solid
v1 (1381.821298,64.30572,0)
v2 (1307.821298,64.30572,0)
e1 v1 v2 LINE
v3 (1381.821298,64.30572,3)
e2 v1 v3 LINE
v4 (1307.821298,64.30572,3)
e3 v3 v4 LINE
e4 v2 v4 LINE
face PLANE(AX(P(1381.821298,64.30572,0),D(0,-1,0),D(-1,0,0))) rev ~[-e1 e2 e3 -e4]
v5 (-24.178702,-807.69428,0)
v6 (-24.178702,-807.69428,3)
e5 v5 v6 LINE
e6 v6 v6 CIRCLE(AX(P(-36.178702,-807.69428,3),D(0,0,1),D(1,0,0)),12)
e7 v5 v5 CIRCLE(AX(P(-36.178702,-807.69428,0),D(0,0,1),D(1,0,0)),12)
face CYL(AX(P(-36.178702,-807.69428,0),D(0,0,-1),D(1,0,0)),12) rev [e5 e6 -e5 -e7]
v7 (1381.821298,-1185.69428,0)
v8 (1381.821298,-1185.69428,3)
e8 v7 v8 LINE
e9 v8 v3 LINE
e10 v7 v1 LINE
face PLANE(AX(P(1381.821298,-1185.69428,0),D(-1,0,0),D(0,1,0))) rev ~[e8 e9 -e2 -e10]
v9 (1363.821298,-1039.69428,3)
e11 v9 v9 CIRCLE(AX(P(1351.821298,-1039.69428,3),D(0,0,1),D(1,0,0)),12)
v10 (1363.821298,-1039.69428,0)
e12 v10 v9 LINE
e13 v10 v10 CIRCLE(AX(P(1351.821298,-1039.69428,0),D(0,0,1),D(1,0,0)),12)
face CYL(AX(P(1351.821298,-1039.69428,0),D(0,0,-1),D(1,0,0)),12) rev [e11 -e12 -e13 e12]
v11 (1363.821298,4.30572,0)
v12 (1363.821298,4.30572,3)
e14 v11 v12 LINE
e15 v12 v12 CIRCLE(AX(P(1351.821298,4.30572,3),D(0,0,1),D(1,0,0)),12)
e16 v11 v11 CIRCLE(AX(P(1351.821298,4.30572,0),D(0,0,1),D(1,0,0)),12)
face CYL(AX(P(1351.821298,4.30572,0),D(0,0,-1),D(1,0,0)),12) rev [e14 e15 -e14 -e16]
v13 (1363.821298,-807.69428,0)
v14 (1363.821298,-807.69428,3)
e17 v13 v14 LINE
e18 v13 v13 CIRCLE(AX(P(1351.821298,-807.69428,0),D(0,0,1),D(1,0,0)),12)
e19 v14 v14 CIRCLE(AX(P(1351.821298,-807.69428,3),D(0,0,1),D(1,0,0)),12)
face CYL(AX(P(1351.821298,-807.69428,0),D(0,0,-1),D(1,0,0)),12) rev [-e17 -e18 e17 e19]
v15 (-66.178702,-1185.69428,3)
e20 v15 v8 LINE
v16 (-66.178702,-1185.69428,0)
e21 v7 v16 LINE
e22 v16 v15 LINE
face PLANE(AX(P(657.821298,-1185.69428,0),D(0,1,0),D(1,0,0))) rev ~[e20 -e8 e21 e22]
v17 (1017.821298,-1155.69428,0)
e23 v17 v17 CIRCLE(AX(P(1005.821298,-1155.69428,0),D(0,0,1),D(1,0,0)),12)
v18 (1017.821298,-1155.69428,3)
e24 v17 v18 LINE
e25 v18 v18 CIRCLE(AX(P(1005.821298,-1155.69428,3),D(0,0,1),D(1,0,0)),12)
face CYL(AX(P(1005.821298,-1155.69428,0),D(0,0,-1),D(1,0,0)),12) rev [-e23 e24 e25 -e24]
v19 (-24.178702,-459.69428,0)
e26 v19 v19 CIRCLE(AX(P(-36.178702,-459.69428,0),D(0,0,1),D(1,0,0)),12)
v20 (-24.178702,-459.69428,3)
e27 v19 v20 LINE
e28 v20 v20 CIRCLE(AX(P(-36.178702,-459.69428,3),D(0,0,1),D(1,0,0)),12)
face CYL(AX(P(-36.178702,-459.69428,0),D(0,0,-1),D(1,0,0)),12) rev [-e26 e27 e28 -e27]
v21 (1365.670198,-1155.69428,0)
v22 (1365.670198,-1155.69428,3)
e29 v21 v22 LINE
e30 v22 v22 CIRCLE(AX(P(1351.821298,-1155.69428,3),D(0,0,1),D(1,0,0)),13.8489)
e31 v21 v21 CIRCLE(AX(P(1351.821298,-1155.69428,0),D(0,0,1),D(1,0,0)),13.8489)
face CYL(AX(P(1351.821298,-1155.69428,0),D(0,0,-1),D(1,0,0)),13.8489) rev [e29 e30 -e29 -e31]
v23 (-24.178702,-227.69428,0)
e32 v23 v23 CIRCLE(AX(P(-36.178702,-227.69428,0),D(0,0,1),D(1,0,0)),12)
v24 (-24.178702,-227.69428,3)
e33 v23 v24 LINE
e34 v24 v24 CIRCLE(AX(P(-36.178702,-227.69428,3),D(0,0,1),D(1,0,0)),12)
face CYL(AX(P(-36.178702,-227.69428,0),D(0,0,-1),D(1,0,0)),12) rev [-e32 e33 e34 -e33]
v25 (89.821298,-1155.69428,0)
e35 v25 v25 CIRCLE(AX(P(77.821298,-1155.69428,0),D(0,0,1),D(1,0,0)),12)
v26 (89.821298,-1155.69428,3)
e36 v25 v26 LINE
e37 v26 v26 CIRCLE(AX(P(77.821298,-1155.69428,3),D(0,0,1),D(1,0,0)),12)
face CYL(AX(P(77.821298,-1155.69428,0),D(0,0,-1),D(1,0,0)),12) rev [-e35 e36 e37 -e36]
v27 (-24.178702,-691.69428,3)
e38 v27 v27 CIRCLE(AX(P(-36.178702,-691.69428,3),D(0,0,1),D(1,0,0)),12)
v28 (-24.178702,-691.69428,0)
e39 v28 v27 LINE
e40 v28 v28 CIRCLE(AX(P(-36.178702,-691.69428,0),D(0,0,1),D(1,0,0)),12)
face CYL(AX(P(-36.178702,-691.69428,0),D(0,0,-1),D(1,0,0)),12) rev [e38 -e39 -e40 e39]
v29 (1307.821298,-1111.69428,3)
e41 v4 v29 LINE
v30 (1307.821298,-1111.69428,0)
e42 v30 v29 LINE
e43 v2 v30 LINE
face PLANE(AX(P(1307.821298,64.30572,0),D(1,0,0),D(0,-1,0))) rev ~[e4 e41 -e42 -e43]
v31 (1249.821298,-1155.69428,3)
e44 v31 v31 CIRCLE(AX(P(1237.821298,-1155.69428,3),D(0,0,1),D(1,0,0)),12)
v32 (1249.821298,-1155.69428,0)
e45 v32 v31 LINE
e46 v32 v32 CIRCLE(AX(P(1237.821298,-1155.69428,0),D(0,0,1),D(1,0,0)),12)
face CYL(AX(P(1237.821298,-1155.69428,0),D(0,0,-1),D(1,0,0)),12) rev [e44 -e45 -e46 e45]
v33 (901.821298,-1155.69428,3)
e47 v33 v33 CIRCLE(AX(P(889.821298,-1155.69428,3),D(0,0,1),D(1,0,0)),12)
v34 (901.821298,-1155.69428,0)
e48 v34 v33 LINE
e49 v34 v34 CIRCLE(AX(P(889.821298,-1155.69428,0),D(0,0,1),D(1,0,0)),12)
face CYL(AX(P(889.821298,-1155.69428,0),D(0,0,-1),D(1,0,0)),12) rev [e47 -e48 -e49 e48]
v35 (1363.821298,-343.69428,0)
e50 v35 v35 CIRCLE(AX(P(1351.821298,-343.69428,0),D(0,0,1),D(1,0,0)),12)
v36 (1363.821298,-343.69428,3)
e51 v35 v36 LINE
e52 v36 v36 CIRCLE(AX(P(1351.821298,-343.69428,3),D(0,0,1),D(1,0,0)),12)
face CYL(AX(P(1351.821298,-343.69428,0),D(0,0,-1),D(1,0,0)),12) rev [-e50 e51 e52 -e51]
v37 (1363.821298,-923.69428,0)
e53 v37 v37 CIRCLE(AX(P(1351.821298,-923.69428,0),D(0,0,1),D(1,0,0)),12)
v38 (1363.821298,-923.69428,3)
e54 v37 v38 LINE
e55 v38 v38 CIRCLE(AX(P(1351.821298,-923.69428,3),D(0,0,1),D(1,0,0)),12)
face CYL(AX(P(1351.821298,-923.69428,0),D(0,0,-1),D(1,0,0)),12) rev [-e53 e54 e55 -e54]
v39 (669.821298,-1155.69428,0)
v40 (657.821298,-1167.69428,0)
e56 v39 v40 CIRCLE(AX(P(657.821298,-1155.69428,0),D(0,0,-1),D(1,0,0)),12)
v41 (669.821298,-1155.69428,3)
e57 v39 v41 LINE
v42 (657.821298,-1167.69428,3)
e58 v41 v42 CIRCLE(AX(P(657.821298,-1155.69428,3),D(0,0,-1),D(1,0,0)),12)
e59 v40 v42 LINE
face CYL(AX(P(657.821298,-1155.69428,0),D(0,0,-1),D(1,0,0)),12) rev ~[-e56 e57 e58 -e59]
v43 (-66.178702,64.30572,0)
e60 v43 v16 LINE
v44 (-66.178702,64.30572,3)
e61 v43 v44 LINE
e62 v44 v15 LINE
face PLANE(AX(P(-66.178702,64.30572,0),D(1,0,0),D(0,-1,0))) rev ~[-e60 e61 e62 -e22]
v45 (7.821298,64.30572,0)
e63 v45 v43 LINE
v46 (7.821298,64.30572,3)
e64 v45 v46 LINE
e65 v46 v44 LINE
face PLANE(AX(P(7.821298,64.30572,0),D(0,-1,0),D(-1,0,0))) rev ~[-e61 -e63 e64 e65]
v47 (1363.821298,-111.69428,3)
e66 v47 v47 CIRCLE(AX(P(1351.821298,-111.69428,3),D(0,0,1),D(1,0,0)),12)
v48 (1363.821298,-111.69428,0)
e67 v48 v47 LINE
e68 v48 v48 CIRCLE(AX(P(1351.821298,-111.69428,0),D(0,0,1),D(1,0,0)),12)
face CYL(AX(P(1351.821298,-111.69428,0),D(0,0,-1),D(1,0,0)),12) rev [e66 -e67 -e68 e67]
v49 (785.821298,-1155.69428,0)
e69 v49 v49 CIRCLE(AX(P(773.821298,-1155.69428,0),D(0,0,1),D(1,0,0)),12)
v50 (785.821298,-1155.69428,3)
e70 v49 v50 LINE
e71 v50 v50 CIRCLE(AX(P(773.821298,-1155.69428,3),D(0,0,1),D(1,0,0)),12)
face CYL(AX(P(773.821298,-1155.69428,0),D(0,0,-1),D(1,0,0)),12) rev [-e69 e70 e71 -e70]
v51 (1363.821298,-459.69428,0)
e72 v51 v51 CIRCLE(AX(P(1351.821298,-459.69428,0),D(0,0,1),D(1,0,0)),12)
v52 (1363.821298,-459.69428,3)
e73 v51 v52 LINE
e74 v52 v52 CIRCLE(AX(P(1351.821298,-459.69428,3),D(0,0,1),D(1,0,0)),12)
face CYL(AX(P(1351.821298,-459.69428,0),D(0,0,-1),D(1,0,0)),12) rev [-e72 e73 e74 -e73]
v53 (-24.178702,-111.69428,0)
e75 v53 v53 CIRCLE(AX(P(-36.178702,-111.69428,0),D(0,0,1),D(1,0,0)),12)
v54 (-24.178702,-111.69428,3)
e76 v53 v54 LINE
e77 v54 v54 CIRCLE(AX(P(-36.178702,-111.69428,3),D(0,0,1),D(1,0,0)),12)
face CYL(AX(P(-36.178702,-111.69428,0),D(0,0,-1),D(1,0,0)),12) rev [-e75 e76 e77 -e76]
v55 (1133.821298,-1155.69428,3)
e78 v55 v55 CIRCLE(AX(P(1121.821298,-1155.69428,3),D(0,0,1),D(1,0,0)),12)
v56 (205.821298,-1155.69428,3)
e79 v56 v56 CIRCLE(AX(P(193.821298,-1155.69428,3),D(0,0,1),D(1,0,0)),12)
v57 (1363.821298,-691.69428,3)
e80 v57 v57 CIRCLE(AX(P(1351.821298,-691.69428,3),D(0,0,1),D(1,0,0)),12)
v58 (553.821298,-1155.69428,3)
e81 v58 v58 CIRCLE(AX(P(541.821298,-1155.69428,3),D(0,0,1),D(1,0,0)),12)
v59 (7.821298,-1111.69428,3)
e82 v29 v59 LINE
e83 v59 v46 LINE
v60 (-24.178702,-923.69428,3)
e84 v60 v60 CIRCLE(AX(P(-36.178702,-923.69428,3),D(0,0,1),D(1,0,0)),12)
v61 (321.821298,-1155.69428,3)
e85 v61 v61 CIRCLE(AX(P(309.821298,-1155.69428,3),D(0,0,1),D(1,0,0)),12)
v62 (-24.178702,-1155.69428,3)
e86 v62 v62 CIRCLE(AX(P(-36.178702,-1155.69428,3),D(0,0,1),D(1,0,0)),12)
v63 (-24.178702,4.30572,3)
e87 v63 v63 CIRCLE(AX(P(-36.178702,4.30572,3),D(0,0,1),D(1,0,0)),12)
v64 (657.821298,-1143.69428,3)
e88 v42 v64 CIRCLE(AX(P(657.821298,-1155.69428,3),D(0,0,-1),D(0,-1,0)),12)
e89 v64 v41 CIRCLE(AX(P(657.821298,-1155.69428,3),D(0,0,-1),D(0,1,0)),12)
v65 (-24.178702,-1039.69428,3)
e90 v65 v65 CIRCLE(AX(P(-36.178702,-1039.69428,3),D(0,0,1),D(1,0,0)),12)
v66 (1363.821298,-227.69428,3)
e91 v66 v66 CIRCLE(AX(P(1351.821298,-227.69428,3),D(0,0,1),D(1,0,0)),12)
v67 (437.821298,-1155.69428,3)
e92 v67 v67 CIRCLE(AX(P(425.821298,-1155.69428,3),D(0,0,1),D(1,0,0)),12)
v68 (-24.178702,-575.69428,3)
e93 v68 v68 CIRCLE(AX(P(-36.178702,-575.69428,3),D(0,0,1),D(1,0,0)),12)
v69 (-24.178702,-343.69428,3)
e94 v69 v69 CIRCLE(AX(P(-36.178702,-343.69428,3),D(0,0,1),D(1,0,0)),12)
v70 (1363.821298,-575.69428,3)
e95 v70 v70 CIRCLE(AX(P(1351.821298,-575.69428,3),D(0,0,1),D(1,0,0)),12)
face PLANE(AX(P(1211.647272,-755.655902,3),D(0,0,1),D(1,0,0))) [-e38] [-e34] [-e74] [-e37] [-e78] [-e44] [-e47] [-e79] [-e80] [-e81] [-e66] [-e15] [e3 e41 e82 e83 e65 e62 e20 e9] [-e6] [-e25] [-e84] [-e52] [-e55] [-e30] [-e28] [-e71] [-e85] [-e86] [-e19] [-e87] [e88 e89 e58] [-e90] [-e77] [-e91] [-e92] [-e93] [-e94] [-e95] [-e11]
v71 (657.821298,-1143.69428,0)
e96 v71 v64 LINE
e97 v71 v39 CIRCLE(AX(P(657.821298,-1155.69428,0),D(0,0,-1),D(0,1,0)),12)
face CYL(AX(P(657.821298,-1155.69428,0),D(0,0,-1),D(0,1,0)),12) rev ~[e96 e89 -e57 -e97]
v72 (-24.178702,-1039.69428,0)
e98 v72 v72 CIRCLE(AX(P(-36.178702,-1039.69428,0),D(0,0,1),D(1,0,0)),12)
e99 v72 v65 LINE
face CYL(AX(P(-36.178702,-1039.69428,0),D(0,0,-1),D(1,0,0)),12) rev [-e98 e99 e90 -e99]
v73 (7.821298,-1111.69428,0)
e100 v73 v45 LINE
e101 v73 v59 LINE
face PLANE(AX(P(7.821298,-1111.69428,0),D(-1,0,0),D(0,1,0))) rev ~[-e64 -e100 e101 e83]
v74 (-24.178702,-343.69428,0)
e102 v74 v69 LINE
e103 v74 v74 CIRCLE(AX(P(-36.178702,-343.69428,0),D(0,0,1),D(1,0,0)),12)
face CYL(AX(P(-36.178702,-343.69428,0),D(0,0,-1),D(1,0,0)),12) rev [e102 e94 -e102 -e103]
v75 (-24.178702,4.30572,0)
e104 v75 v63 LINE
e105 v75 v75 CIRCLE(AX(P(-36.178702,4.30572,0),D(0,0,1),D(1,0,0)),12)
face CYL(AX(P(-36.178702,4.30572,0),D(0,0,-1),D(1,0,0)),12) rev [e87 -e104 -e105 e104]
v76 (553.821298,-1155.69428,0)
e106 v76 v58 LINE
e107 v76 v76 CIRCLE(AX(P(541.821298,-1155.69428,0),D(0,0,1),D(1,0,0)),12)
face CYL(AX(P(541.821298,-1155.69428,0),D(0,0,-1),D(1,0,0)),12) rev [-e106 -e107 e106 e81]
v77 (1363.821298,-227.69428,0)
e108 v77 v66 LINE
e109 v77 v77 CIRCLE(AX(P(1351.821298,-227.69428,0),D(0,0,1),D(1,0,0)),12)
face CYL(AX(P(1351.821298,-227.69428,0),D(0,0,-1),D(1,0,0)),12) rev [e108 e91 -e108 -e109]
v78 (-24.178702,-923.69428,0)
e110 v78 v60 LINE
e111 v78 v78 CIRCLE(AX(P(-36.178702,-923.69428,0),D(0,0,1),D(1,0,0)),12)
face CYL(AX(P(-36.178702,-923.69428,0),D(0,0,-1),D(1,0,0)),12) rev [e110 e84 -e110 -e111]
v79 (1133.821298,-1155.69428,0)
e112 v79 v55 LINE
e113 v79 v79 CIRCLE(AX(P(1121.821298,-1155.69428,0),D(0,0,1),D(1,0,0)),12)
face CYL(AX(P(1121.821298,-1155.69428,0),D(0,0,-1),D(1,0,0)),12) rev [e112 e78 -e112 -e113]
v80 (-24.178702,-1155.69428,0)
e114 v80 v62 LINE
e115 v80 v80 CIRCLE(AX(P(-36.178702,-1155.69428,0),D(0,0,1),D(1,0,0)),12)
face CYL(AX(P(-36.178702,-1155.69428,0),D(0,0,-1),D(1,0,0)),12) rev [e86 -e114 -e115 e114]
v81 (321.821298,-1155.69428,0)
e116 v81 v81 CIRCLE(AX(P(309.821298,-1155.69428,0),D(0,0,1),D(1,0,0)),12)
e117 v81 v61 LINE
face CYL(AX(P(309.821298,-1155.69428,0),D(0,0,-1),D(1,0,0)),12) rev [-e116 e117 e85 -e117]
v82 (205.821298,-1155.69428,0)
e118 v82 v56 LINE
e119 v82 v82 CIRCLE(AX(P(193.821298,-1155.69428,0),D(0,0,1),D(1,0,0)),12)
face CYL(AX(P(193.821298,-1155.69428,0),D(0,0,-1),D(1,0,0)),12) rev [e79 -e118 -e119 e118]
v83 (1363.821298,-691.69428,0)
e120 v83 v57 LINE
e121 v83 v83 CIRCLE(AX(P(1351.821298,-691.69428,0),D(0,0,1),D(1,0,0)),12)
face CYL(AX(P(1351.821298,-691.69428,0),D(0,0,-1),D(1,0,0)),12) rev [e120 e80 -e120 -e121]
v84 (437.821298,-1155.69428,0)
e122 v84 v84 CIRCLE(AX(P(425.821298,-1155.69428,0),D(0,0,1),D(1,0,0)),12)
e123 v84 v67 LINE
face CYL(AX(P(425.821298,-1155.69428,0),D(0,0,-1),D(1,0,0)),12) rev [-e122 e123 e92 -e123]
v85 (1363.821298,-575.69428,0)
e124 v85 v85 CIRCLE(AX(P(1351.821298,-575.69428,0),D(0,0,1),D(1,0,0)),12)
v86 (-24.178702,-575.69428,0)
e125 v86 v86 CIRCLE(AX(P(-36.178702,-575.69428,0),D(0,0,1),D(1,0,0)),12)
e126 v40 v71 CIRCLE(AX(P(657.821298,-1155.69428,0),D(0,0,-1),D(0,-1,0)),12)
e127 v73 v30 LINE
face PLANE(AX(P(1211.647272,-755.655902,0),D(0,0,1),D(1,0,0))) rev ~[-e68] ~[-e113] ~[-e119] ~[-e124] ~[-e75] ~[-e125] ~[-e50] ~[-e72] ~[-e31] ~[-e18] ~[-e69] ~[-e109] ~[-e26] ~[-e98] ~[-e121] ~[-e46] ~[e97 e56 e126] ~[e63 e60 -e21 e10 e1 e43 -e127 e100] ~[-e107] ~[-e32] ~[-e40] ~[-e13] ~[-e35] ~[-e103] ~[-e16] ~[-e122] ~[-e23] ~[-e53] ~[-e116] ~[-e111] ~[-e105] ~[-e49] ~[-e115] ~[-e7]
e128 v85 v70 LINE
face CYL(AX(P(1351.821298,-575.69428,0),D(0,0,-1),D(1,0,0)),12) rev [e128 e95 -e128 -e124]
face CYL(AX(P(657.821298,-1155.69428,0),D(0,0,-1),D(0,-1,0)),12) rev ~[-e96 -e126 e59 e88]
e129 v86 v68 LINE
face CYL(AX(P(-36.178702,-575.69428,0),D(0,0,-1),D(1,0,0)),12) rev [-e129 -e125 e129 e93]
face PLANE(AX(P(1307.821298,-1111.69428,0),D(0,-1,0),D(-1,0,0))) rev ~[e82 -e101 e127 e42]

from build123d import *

# Parameters (mm, degrees)
SKETCH1_R           = 12
SKETCH1_R_2         = 13.848900056
BOSS_EXTRUDE1_DEPTH = 3


with BuildPart() as part:
    # Sketch1 → Boss-Extrude1 (new body)
    # profile 1 of 2: a face of its own
    with BuildSketch(Plane.XY):
        with BuildLine():
            Line((7.821297611, 64.305720246), (-66.178702389, 64.305720246))
            Line((-66.178702389, 64.305720246), (-66.178702389, -1185.694279754))
            Line((-66.178702389, -1185.694279754), (657.821297611, -1185.694279754))
            Line((657.821297611, -1185.694279754), (657.821297611, -1167.694279754))
            ThreePointArc((657.821297611, -1167.694279754), (645.821297611, -1155.694279754), (657.821297611, -1143.694279754))
            Line((657.821297611, -1143.694279754), (657.821297611, -1111.694279754))
            Line((657.821297611, -1111.694279754), (7.821297611, -1111.694279754))
            Line((7.821297611, -1111.694279754), (7.821297611, 64.305720246))
        make_face()
        with Locations((-36.178702389, -1155.694279754)):
            Circle(SKETCH1_R, mode=Mode.SUBTRACT)
        with Locations((77.821297611, -1155.694279754)):
            Circle(SKETCH1_R, mode=Mode.SUBTRACT)
        with Locations((-36.178702389, -1039.694279754)):
            Circle(SKETCH1_R, mode=Mode.SUBTRACT)
        with Locations((193.821297611, -1155.694279754)):
            Circle(SKETCH1_R, mode=Mode.SUBTRACT)
        with Locations((-36.178702389, -923.694279754)):
            Circle(SKETCH1_R, mode=Mode.SUBTRACT)
        with Locations((309.821297611, -1155.694279754)):
            Circle(SKETCH1_R, mode=Mode.SUBTRACT)
        with Locations((425.821297611, -1155.694279754)):
            Circle(SKETCH1_R, mode=Mode.SUBTRACT)
        with Locations((541.821297611, -1155.694279754)):
            Circle(SKETCH1_R, mode=Mode.SUBTRACT)
        with Locations((-36.178702389, -807.694279754)):
            Circle(SKETCH1_R, mode=Mode.SUBTRACT)
        with Locations((-36.178702389, -691.694279754)):
            Circle(SKETCH1_R, mode=Mode.SUBTRACT)
        with Locations((-36.178702389, -575.694279754)):
            Circle(SKETCH1_R, mode=Mode.SUBTRACT)
        with Locations((-36.178702389, -459.694279754)):
            Circle(SKETCH1_R, mode=Mode.SUBTRACT)
        with Locations((-36.178702389, -343.694279754)):
            Circle(SKETCH1_R, mode=Mode.SUBTRACT)
        with Locations((-36.178702389, -227.694279754)):
            Circle(SKETCH1_R, mode=Mode.SUBTRACT)
        with Locations((-36.178702389, -111.694279754)):
            Circle(SKETCH1_R, mode=Mode.SUBTRACT)
        with Locations((-36.178702389, 4.305720246)):
            Circle(SKETCH1_R, mode=Mode.SUBTRACT)
    # profile 2 of 2: a face of its own
    with BuildSketch(Plane.XY):
        with BuildLine():
            Line((657.821297611, -1167.694279754), (657.821297611, -1185.694279754))
            Line((657.821297611, -1185.694279754), (1381.821297611, -1185.694279754))
            Line((1381.821297611, -1185.694279754), (1381.821297611, 64.305720246))
            Line((1381.821297611, 64.305720246), (1307.821297611, 64.305720246))
            Line((1307.821297611, 64.305720246), (1307.821297611, -1111.694279754))
            Line((1307.821297611, -1111.694279754), (657.821297611, -1111.694279754))
            Line((657.821297611, -1111.694279754), (657.821297611, -1143.694279754))
            ThreePointArc((657.821297611, -1143.694279754), (666.306578985, -1147.20899838), (669.821297611, -1155.694279754))
            ThreePointArc((669.821297611, -1155.694279754), (666.306578985, -1164.179561128), (657.821297611, -1167.694279754))
        make_face()
        with Locations((773.821297611, -1155.694279754)):
            Circle(SKETCH1_R, mode=Mode.SUBTRACT)
        with Locations((889.821297611, -1155.694279754)):
            Circle(SKETCH1_R, mode=Mode.SUBTRACT)
        with Locations((1005.821297611, -1155.694279754)):
            Circle(SKETCH1_R, mode=Mode.SUBTRACT)
        with Locations((1121.821297611, -1155.694279754)):
            Circle(SKETCH1_R, mode=Mode.SUBTRACT)
        with Locations((1237.821297611, -1155.694279754)):
            Circle(SKETCH1_R, mode=Mode.SUBTRACT)
        with Locations((1351.821297611, -1155.694279754)):
            Circle(SKETCH1_R_2, mode=Mode.SUBTRACT)
        with Locations((1351.821297611, -1039.694279754)):
            Circle(SKETCH1_R, mode=Mode.SUBTRACT)
        with Locations((1351.821297611, -923.694279754)):
            Circle(SKETCH1_R, mode=Mode.SUBTRACT)
        with Locations((1351.821297611, -807.694279754)):
            Circle(SKETCH1_R, mode=Mode.SUBTRACT)
        with Locations((1351.821297611, -691.694279754)):
            Circle(SKETCH1_R, mode=Mode.SUBTRACT)
        with Locations((1351.821297611, -575.694279754)):
            Circle(SKETCH1_R, mode=Mode.SUBTRACT)
        with Locations((1351.821297611, -459.694279754)):
            Circle(SKETCH1_R, mode=Mode.SUBTRACT)
        with Locations((1351.821297611, -343.694279754)):
            Circle(SKETCH1_R, mode=Mode.SUBTRACT)
        with Locations((1351.821297611, -227.694279754)):
            Circle(SKETCH1_R, mode=Mode.SUBTRACT)
        with Locations((1351.821297611, -111.694279754)):
            Circle(SKETCH1_R, mode=Mode.SUBTRACT)
        with Locations((1351.821297611, 4.305720246)):
            Circle(SKETCH1_R, mode=Mode.SUBTRACT)
    extrude(amount=BOSS_EXTRUDE1_DEPTH)


solid = part.part
